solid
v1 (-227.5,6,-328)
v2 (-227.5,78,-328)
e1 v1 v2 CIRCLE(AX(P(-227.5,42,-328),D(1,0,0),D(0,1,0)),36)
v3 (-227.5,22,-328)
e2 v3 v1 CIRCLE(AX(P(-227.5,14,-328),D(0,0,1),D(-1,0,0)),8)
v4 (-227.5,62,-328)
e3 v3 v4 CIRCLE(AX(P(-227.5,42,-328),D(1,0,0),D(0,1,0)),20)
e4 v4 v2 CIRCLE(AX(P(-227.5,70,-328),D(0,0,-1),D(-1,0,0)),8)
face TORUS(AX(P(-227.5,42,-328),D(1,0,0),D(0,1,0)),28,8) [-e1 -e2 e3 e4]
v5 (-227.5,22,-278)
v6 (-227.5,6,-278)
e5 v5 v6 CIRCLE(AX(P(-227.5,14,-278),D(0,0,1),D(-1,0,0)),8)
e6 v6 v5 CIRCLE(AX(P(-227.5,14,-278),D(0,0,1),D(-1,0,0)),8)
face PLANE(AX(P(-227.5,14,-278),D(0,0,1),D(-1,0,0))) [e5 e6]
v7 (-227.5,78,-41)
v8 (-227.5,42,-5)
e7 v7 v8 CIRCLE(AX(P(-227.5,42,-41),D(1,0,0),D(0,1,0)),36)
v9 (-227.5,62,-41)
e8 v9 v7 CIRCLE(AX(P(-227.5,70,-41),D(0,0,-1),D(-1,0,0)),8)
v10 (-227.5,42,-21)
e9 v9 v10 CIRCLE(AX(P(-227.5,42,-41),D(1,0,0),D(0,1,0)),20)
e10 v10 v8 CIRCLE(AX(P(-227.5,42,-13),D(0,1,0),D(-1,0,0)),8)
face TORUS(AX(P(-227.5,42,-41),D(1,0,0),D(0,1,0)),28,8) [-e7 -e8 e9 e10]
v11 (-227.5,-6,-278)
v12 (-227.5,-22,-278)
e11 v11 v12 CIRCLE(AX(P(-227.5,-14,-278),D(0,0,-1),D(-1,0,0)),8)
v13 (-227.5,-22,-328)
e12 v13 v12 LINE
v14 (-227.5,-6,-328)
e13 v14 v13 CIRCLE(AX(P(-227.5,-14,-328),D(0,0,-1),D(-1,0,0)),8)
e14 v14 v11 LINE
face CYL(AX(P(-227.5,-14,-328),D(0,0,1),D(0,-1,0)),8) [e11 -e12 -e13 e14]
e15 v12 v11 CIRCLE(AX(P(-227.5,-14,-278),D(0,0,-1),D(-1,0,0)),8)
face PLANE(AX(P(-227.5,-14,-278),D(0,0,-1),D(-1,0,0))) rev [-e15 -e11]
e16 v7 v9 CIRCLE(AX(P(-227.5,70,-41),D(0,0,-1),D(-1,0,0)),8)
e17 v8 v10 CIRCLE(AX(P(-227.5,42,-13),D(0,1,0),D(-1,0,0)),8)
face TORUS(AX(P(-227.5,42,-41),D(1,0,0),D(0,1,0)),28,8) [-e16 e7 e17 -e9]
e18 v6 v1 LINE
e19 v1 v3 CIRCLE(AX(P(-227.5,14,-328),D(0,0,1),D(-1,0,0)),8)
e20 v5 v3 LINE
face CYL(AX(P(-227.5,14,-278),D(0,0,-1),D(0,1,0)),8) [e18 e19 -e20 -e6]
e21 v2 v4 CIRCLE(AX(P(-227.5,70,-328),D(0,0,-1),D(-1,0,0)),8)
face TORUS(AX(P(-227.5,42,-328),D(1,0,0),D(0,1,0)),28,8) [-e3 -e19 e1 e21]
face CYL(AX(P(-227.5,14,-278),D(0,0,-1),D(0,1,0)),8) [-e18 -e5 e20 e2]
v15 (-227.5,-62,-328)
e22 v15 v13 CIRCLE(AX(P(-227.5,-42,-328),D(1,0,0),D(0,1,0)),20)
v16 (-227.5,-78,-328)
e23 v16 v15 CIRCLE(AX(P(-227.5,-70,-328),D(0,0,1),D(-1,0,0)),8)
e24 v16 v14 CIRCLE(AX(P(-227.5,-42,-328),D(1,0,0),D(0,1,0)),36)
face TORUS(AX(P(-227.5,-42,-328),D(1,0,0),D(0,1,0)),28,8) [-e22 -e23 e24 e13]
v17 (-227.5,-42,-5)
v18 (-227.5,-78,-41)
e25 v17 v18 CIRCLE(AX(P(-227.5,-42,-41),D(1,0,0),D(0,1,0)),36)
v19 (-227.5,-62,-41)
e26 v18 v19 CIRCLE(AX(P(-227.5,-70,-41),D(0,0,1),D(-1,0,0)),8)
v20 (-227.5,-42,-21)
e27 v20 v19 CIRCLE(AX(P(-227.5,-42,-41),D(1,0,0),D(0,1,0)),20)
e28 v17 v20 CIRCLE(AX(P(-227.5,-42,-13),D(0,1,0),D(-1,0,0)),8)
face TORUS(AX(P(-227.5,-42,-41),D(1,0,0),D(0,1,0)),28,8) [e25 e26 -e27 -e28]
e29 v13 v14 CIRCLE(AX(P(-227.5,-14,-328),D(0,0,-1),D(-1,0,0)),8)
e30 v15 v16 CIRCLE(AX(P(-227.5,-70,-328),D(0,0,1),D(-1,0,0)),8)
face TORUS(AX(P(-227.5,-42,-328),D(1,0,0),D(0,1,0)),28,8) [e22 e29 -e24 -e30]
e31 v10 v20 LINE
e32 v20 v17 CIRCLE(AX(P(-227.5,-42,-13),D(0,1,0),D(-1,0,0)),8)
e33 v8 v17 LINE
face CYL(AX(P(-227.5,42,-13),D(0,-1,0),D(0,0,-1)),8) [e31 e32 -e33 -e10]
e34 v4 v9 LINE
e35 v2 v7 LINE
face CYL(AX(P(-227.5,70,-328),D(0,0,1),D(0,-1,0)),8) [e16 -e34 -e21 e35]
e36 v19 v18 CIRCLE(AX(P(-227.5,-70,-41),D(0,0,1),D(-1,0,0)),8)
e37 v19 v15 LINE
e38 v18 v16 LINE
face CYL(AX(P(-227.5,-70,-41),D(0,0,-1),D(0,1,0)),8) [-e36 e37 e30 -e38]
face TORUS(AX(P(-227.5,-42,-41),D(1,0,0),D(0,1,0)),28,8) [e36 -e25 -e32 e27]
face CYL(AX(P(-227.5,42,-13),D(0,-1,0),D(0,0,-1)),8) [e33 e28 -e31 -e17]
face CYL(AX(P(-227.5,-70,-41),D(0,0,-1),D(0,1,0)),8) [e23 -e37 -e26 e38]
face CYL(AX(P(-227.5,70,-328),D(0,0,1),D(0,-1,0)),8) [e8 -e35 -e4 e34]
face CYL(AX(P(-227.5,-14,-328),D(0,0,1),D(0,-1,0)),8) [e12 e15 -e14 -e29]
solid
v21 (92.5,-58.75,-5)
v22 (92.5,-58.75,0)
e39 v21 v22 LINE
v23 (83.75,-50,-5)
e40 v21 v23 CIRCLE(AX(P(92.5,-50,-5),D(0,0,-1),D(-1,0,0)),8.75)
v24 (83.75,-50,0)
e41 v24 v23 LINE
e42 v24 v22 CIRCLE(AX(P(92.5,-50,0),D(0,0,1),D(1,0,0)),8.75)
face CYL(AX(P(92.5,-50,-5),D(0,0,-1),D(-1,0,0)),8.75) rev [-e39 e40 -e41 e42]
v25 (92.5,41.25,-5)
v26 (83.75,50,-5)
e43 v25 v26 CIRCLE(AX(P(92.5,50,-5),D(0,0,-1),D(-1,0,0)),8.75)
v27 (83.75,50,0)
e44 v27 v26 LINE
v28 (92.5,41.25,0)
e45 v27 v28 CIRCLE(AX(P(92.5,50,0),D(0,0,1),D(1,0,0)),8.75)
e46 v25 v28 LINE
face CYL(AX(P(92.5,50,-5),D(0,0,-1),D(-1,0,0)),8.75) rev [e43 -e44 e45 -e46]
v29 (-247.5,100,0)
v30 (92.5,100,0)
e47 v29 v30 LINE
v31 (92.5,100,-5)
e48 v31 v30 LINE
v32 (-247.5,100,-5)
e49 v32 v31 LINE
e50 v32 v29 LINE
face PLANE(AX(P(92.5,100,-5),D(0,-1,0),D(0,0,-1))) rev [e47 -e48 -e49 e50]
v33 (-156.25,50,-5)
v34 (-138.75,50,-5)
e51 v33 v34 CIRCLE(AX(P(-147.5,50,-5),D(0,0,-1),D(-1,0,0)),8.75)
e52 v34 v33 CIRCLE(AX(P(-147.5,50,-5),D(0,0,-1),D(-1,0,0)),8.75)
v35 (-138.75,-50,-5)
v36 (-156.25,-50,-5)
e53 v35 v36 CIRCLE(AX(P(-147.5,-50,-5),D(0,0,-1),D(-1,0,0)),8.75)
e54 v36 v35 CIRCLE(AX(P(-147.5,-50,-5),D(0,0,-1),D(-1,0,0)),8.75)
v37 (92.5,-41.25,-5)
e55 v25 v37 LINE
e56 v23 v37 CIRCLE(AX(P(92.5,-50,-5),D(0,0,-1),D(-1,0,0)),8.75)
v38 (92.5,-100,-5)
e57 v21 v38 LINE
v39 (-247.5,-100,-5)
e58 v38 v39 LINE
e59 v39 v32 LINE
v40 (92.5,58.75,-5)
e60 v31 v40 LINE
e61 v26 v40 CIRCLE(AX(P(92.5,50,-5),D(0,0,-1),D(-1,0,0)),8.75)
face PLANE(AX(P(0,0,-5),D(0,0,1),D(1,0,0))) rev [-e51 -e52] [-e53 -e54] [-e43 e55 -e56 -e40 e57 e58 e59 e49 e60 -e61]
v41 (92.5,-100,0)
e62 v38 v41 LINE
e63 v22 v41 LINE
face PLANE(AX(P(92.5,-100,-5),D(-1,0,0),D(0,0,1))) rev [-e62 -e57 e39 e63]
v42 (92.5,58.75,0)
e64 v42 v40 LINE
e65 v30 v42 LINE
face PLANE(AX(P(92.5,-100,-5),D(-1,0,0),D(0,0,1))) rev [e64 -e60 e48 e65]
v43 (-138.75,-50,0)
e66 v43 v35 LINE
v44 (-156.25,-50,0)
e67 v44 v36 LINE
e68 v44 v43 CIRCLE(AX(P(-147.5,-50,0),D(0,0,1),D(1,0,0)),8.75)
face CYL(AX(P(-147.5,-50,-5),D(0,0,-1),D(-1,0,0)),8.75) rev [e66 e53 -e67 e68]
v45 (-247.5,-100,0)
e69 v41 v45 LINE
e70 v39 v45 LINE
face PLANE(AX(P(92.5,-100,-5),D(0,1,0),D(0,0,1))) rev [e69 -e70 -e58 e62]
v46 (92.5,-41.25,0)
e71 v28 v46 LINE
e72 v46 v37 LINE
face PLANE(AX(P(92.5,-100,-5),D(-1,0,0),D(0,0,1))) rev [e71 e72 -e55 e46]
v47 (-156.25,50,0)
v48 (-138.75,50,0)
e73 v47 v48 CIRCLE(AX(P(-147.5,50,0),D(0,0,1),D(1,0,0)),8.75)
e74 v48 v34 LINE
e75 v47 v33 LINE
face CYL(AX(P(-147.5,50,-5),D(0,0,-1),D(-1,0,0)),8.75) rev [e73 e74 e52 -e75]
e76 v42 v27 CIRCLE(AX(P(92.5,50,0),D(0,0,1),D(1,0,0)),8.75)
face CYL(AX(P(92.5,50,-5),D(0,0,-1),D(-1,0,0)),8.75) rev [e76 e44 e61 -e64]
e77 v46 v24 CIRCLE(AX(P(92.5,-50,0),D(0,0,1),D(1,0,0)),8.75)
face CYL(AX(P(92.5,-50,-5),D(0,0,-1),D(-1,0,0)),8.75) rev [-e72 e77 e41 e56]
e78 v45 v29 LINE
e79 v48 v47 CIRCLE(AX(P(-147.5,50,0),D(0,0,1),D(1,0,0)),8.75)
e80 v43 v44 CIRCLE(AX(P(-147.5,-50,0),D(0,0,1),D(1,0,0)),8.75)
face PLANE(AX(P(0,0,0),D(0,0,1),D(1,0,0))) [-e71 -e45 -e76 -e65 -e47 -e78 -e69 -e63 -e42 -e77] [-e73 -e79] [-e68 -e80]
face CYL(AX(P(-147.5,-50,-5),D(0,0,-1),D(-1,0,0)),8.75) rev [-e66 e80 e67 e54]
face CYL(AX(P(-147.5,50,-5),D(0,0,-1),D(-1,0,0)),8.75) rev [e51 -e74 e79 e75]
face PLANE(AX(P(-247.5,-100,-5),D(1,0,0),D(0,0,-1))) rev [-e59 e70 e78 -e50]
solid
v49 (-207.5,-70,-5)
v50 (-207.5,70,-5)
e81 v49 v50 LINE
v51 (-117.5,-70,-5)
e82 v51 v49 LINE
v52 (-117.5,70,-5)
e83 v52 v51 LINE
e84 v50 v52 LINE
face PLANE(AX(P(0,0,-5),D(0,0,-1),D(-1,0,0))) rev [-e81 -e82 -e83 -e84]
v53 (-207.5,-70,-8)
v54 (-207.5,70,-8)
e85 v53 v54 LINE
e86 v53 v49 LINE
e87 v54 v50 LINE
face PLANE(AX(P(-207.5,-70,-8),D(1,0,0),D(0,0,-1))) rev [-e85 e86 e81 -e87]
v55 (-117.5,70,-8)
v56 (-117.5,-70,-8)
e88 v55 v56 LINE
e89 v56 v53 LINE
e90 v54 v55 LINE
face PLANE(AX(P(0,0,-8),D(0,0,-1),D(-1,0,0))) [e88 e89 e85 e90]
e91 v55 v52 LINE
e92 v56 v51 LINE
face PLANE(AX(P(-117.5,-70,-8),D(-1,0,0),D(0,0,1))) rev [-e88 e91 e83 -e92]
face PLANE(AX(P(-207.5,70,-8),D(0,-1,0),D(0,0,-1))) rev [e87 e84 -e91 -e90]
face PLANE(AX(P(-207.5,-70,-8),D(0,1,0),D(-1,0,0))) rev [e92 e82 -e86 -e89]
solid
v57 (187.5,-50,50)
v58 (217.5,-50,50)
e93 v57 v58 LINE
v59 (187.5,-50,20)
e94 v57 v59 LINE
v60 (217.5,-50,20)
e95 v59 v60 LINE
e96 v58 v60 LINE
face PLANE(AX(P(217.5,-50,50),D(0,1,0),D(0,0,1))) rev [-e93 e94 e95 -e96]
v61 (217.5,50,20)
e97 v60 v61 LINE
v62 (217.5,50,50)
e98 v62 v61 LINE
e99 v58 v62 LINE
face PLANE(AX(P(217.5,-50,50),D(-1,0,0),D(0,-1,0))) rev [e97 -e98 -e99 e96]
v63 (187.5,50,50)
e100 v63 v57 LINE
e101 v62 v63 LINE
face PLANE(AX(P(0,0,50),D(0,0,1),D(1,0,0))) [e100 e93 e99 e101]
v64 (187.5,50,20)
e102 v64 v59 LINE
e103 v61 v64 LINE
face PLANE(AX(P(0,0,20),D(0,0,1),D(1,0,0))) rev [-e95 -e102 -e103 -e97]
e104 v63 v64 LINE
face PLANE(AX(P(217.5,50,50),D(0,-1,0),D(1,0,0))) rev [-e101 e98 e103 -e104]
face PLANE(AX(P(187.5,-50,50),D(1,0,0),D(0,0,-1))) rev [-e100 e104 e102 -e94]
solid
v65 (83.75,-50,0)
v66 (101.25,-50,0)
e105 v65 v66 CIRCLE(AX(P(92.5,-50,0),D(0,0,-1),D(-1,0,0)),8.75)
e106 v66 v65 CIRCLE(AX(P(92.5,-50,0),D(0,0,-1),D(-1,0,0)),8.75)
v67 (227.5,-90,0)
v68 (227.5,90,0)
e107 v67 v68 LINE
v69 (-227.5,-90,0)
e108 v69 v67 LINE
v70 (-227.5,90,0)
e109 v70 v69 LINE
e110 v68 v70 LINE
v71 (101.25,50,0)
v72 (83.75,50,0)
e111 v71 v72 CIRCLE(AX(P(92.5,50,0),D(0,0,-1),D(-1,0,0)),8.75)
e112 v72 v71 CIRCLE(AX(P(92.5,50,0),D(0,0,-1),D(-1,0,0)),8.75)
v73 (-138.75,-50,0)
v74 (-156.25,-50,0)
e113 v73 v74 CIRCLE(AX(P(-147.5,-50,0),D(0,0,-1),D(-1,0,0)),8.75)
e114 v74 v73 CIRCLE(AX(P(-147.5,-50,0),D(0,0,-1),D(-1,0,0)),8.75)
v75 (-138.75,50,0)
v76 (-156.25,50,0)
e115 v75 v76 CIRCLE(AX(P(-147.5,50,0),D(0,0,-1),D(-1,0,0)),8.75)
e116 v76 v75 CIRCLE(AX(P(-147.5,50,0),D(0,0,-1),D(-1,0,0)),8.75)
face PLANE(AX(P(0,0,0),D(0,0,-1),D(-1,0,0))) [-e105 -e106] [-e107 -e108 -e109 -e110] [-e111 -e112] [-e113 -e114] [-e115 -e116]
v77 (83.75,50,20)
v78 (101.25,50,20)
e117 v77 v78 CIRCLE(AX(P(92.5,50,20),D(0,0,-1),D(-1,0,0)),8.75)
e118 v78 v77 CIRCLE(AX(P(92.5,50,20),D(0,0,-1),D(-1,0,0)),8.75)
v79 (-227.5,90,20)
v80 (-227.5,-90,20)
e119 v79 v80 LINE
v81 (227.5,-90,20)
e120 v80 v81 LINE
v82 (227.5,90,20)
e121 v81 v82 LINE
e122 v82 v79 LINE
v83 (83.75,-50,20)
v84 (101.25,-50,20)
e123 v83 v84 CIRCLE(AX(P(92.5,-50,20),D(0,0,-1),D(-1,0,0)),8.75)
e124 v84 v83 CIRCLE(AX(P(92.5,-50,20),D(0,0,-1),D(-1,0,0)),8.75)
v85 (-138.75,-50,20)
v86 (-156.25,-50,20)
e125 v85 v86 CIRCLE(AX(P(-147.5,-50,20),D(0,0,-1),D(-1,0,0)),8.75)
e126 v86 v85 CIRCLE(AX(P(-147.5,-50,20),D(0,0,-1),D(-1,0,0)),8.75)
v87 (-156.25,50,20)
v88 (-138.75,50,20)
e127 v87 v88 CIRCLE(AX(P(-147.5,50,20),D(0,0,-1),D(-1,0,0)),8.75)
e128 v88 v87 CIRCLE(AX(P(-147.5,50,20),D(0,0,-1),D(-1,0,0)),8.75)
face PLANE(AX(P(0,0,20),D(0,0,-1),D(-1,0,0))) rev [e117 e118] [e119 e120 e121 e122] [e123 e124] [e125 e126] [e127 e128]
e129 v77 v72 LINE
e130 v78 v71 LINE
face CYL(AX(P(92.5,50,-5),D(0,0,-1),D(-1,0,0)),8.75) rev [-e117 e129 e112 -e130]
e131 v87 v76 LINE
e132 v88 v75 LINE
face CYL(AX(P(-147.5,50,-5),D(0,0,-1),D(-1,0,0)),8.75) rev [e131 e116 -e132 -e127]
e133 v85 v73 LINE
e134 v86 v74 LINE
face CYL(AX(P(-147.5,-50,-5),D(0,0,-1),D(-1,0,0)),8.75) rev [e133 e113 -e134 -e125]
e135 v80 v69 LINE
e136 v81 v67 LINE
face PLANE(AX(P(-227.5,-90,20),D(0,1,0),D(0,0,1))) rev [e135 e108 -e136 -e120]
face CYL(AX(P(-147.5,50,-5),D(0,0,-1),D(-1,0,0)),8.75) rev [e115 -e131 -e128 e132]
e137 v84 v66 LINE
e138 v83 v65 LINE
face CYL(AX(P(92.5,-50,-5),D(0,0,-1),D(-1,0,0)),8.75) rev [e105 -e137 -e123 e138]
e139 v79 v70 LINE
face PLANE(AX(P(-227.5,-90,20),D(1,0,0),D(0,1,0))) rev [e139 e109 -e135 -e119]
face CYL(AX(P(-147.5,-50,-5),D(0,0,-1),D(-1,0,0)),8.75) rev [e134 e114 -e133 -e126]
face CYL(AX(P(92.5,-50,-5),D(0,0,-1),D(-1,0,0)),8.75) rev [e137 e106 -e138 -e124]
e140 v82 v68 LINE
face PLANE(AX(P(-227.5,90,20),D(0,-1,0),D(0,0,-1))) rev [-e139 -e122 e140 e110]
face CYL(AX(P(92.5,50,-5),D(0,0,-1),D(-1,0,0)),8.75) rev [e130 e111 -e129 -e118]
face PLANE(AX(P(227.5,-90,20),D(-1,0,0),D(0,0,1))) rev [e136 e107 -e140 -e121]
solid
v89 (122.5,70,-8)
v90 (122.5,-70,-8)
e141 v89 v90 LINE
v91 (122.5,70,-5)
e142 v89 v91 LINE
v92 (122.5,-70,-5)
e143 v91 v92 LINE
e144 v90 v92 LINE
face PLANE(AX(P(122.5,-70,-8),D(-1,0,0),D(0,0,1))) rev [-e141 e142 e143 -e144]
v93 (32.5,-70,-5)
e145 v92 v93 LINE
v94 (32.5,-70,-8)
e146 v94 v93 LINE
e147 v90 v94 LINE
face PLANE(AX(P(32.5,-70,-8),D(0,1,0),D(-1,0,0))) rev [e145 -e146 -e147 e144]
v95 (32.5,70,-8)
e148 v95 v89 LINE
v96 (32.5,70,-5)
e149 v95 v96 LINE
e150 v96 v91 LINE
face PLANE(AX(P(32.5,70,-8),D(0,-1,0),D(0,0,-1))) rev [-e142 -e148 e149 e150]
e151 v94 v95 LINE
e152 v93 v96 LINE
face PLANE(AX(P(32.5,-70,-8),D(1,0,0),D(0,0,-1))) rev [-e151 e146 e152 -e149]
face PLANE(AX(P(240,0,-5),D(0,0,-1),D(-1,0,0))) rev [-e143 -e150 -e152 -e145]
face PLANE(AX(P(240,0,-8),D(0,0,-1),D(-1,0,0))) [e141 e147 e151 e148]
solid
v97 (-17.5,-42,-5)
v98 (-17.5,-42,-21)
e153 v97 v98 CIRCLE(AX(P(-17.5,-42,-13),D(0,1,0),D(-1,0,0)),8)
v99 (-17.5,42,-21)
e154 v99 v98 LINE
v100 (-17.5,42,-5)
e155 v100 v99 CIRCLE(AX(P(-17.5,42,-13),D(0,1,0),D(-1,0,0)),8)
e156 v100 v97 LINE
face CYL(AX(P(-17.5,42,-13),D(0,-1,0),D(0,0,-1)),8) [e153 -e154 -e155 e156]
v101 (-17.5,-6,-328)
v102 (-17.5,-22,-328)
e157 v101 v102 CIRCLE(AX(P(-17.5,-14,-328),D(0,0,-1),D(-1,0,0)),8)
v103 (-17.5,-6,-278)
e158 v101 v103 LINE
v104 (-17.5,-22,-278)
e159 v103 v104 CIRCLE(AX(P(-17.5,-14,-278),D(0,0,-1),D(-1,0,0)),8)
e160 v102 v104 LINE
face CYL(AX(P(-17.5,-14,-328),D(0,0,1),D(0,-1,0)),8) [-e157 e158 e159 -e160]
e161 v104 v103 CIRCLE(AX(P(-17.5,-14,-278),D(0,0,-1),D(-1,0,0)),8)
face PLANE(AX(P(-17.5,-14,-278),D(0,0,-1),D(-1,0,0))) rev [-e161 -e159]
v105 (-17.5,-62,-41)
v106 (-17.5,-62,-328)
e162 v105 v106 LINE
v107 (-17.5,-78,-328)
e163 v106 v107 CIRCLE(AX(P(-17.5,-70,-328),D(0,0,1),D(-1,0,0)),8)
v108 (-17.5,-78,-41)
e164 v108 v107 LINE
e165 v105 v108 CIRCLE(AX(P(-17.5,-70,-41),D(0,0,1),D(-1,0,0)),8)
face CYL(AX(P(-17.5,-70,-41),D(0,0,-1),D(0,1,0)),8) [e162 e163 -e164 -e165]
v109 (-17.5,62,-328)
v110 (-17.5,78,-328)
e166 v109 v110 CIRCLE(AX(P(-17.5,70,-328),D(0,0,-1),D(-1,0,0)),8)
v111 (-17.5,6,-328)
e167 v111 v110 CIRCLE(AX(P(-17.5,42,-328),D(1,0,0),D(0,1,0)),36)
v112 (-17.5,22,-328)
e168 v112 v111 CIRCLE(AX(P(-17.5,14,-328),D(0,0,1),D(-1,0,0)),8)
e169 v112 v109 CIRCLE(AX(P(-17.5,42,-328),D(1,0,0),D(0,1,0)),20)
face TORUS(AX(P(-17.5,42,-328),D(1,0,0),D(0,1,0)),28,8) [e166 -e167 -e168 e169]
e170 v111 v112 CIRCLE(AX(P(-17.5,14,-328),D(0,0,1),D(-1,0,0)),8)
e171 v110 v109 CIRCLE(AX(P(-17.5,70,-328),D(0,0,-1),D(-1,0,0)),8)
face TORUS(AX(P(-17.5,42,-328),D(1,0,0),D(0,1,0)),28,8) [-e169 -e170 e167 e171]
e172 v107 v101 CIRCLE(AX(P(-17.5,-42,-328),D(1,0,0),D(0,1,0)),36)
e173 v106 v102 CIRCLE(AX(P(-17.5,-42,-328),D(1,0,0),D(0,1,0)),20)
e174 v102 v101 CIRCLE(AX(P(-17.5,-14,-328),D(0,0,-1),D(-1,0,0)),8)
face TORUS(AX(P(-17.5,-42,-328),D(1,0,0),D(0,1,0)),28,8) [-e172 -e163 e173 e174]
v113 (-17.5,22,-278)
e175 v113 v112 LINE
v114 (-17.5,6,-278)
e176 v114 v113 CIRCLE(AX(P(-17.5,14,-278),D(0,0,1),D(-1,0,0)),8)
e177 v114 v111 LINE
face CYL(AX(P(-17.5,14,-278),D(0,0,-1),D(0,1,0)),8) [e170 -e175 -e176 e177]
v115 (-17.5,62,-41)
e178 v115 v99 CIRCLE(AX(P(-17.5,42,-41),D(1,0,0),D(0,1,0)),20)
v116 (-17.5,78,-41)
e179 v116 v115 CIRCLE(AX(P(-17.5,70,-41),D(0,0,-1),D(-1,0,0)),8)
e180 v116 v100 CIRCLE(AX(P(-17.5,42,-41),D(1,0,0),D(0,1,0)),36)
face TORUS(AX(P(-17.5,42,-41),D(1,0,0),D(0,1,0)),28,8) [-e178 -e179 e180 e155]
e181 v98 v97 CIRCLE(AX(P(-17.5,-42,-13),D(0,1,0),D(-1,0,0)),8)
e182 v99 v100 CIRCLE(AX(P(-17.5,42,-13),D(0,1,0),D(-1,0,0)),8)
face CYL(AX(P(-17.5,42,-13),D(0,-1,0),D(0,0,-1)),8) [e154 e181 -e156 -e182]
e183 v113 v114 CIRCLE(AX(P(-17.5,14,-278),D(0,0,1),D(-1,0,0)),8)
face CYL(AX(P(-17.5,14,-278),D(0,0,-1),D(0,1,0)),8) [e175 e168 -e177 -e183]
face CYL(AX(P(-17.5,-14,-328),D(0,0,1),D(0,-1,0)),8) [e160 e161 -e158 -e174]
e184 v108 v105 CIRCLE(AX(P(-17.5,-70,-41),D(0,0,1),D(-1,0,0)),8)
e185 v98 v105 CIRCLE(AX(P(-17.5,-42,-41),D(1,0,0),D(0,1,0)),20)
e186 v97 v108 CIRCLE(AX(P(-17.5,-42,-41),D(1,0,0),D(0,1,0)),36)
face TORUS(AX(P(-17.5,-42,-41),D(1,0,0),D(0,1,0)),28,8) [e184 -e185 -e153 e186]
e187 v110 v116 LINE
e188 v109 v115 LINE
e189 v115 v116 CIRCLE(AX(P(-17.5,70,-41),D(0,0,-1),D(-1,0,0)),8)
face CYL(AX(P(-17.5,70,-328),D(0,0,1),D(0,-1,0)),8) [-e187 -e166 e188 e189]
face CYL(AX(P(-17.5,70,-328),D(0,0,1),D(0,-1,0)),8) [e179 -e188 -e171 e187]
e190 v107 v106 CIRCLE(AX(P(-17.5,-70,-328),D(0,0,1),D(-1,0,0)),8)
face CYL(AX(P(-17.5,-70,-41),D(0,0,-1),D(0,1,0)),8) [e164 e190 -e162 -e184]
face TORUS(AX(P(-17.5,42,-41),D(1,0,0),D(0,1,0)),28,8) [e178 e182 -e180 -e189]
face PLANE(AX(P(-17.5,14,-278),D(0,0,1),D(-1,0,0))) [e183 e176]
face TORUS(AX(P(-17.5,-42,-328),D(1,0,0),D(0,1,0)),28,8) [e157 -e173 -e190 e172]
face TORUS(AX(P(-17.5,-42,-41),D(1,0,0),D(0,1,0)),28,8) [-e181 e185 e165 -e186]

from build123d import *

# Parameters (mm, degrees)
SKETCH_1_W                   = 455
SKETCH_1_H                   = 180
EXTRUDE_1_DEPTH              = 20
SKETCH_2_W                   = 30
SKETCH_2_H                   = 100
EXTRUDE_2_DEPTH              = 30
SKETCH_3_W                   = 340
SKETCH_3_H                   = 200
EXTRUDE_3_DEPTH              = 5
SWEEP_1_PROFILE_R            = 8
PATTERN_LINEAR_1_COUNT       = 2
PATTERN_LINEAR_1_PITCH       = 210
HOLE_WIZARD_M20_1_AT_2_COUNT = 2
HOLE_WIZARD_M20_1_AT_2_PITCH = 240
HOLE_WIZARD_M20_1_AT_3_COUNT = 2
HOLE_WIZARD_M20_1_AT_3_PITCH = 260
HOLE_WIZARD_M20_1_AT_4_COUNT = 2
HOLE_WIZARD_M20_1_AT_4_PITCH = 100
SKETCH_8_W                   = 90
SKETCH_8_H                   = 140
EXTRUDE_4_DEPTH              = 3
PATTERN_LINEAR_2_COUNT       = 2
PATTERN_LINEAR_2_PITCH       = 240


with BuildPart() as part:
    # 草图1 → 凸台-拉伸1 (new body)
    with BuildSketch(Plane.XY):
        Rectangle(SKETCH_1_W, SKETCH_1_H)
    extrude(amount=EXTRUDE_1_DEPTH)


with BuildPart() as body_2:
    # 草图2 → 凸台-拉伸2 (new body)
    with BuildSketch(Plane.XY.offset(20)):
        with Locations((202.5, 0)):
            Rectangle(SKETCH_2_W, SKETCH_2_H)
    extrude(amount=EXTRUDE_2_DEPTH)


with BuildPart() as body_3:
    # 草图3 → 凸台-拉伸3 (new body)
    with BuildSketch(Plane(origin=(0, 0, 0), x_dir=(-1, 0, 0), z_dir=(0, 0, -1))):
        with Locations((77.5, 0)):
            Rectangle(SKETCH_3_W, SKETCH_3_H)
    extrude(amount=EXTRUDE_3_DEPTH)


with BuildPart() as body_4:
    # 扫描1: sweep along a path in 草图4
    with BuildLine(Plane.ZY.offset(227.5)) as sweep_1_path:
        Line((-278, 14), (-328, 14))
        ThreePointArc((-328, 14), (-356, 42), (-328, 70))
        Line((-328, 70), (-41, 70))
        ThreePointArc((-41, 70), (-21.201010127, 61.798989873), (-13, 42))
        Line((-13, 42), (-13, -42))
        ThreePointArc((-13, -42), (-21.201010127, -61.798989873), (-41, -70))
        Line((-41, -70), (-328, -70))
        ThreePointArc((-328, -70), (-356, -42), (-328, -14))
        Line((-328, -14), (-278, -14))
    # 扫描1 profile (on start of the path) → 扫描1 (sweep)
    with BuildSketch(Plane(origin=(-227.5, 14, -278), x_dir=(0, -1, 0), z_dir=(0, 0, -1))):
        Circle(SWEEP_1_PROFILE_R)
    sweep(path=sweep_1_path.line)


with BuildPart() as pattern_linear_1_1:
    # 阵列(线性)1: pattern copy
    add(body_4.part.moved(Location(Vector(1, 0, 0) * (1 * PATTERN_LINEAR_1_PITCH))))


with BuildPart() as hole_wizard_m20_1_tool:
    # 草图7 → M20 螺纹孔1 (revolve)
    with BuildSketch(Plane(origin=(92.5, -50, -5), x_dir=(0, 1, 0), z_dir=(1, 0, 0))):
        Polygon((0, 0), (0, 57.757530416), (8.75, 52.5), (8.75, 0), align=None)
    hole_wizard_m20_1 = revolve(axis=Axis((92.5, -50, -11.35), (0, 0, 1)))


with BuildPart() as part_1:
    add(part.part)

    # M20 螺纹孔1: cut by hole_wizard_m20_1_tool
    add(hole_wizard_m20_1_tool.part, mode=Mode.SUBTRACT)


with BuildPart() as body_3_1:
    add(body_3.part)

    # M20 螺纹孔1: cut by hole_wizard_m20_1_tool
    add(hole_wizard_m20_1_tool.part, mode=Mode.SUBTRACT)


with BuildPart() as hole_wizard_m20_1_at_2_tool:
    # M20 螺纹孔1 at 2: M20 螺纹孔1 ×2
    with Locations(*[(-i * HOLE_WIZARD_M20_1_AT_2_PITCH, 0, 0) for i in range(1, HOLE_WIZARD_M20_1_AT_2_COUNT)]):
        add(hole_wizard_m20_1)


with BuildPart() as part_2:
    add(part_1.part)

    # M20 螺纹孔1 at 2: cut by hole_wizard_m20_1_at_2_tool
    add(hole_wizard_m20_1_at_2_tool.part, mode=Mode.SUBTRACT)


with BuildPart() as body_3_2:
    add(body_3_1.part)

    # M20 螺纹孔1 at 2: cut by hole_wizard_m20_1_at_2_tool
    add(hole_wizard_m20_1_at_2_tool.part, mode=Mode.SUBTRACT)


with BuildPart() as hole_wizard_m20_1_at_3_tool:
    # M20 螺纹孔1 at 3: M20 螺纹孔1 ×2
    with Locations(*[Vector(-0.9230769230769229, 0.3846153846153851, 0) * (i * HOLE_WIZARD_M20_1_AT_3_PITCH) for i in range(1, HOLE_WIZARD_M20_1_AT_3_COUNT)]):
        add(hole_wizard_m20_1)


with BuildPart() as part_3:
    add(part_2.part)

    # M20 螺纹孔1 at 3: cut by hole_wizard_m20_1_at_3_tool
    add(hole_wizard_m20_1_at_3_tool.part, mode=Mode.SUBTRACT)


with BuildPart() as body_3_3:
    add(body_3_2.part)

    # M20 螺纹孔1 at 3: cut by hole_wizard_m20_1_at_3_tool
    add(hole_wizard_m20_1_at_3_tool.part, mode=Mode.SUBTRACT)


with BuildPart() as hole_wizard_m20_1_at_4_tool:
    # M20 螺纹孔1 at 4: M20 螺纹孔1 ×2
    with Locations(*[(0, i * HOLE_WIZARD_M20_1_AT_4_PITCH, 0) for i in range(1, HOLE_WIZARD_M20_1_AT_4_COUNT)]):
        add(hole_wizard_m20_1)


with BuildPart() as part_4:
    add(part_3.part)

    # M20 螺纹孔1 at 4: cut by hole_wizard_m20_1_at_4_tool
    add(hole_wizard_m20_1_at_4_tool.part, mode=Mode.SUBTRACT)


with BuildPart() as body_3_4:
    add(body_3_3.part)

    # M20 螺纹孔1 at 4: cut by hole_wizard_m20_1_at_4_tool
    add(hole_wizard_m20_1_at_4_tool.part, mode=Mode.SUBTRACT)


with BuildPart() as body_6:
    # 草图8 → 凸台-拉伸4 (new body)
    with BuildSketch(Plane(origin=(0, 0, -5), x_dir=(-1, 0, 0), z_dir=(0, 0, -1))):
        with Locations((162.5, 0)):
            Rectangle(SKETCH_8_W, SKETCH_8_H)
    extrude(amount=EXTRUDE_4_DEPTH)


with BuildPart() as pattern_linear_2_1:
    # 阵列(线性)2: pattern copy
    add(body_6.part.moved(Location(Vector(1, 0, 0) * (1 * PATTERN_LINEAR_2_PITCH))))


solid = Compound([body_2.part, body_4.part, pattern_linear_1_1.part, part_4.part, body_3_4.part, body_6.part, pattern_linear_2_1.part])
